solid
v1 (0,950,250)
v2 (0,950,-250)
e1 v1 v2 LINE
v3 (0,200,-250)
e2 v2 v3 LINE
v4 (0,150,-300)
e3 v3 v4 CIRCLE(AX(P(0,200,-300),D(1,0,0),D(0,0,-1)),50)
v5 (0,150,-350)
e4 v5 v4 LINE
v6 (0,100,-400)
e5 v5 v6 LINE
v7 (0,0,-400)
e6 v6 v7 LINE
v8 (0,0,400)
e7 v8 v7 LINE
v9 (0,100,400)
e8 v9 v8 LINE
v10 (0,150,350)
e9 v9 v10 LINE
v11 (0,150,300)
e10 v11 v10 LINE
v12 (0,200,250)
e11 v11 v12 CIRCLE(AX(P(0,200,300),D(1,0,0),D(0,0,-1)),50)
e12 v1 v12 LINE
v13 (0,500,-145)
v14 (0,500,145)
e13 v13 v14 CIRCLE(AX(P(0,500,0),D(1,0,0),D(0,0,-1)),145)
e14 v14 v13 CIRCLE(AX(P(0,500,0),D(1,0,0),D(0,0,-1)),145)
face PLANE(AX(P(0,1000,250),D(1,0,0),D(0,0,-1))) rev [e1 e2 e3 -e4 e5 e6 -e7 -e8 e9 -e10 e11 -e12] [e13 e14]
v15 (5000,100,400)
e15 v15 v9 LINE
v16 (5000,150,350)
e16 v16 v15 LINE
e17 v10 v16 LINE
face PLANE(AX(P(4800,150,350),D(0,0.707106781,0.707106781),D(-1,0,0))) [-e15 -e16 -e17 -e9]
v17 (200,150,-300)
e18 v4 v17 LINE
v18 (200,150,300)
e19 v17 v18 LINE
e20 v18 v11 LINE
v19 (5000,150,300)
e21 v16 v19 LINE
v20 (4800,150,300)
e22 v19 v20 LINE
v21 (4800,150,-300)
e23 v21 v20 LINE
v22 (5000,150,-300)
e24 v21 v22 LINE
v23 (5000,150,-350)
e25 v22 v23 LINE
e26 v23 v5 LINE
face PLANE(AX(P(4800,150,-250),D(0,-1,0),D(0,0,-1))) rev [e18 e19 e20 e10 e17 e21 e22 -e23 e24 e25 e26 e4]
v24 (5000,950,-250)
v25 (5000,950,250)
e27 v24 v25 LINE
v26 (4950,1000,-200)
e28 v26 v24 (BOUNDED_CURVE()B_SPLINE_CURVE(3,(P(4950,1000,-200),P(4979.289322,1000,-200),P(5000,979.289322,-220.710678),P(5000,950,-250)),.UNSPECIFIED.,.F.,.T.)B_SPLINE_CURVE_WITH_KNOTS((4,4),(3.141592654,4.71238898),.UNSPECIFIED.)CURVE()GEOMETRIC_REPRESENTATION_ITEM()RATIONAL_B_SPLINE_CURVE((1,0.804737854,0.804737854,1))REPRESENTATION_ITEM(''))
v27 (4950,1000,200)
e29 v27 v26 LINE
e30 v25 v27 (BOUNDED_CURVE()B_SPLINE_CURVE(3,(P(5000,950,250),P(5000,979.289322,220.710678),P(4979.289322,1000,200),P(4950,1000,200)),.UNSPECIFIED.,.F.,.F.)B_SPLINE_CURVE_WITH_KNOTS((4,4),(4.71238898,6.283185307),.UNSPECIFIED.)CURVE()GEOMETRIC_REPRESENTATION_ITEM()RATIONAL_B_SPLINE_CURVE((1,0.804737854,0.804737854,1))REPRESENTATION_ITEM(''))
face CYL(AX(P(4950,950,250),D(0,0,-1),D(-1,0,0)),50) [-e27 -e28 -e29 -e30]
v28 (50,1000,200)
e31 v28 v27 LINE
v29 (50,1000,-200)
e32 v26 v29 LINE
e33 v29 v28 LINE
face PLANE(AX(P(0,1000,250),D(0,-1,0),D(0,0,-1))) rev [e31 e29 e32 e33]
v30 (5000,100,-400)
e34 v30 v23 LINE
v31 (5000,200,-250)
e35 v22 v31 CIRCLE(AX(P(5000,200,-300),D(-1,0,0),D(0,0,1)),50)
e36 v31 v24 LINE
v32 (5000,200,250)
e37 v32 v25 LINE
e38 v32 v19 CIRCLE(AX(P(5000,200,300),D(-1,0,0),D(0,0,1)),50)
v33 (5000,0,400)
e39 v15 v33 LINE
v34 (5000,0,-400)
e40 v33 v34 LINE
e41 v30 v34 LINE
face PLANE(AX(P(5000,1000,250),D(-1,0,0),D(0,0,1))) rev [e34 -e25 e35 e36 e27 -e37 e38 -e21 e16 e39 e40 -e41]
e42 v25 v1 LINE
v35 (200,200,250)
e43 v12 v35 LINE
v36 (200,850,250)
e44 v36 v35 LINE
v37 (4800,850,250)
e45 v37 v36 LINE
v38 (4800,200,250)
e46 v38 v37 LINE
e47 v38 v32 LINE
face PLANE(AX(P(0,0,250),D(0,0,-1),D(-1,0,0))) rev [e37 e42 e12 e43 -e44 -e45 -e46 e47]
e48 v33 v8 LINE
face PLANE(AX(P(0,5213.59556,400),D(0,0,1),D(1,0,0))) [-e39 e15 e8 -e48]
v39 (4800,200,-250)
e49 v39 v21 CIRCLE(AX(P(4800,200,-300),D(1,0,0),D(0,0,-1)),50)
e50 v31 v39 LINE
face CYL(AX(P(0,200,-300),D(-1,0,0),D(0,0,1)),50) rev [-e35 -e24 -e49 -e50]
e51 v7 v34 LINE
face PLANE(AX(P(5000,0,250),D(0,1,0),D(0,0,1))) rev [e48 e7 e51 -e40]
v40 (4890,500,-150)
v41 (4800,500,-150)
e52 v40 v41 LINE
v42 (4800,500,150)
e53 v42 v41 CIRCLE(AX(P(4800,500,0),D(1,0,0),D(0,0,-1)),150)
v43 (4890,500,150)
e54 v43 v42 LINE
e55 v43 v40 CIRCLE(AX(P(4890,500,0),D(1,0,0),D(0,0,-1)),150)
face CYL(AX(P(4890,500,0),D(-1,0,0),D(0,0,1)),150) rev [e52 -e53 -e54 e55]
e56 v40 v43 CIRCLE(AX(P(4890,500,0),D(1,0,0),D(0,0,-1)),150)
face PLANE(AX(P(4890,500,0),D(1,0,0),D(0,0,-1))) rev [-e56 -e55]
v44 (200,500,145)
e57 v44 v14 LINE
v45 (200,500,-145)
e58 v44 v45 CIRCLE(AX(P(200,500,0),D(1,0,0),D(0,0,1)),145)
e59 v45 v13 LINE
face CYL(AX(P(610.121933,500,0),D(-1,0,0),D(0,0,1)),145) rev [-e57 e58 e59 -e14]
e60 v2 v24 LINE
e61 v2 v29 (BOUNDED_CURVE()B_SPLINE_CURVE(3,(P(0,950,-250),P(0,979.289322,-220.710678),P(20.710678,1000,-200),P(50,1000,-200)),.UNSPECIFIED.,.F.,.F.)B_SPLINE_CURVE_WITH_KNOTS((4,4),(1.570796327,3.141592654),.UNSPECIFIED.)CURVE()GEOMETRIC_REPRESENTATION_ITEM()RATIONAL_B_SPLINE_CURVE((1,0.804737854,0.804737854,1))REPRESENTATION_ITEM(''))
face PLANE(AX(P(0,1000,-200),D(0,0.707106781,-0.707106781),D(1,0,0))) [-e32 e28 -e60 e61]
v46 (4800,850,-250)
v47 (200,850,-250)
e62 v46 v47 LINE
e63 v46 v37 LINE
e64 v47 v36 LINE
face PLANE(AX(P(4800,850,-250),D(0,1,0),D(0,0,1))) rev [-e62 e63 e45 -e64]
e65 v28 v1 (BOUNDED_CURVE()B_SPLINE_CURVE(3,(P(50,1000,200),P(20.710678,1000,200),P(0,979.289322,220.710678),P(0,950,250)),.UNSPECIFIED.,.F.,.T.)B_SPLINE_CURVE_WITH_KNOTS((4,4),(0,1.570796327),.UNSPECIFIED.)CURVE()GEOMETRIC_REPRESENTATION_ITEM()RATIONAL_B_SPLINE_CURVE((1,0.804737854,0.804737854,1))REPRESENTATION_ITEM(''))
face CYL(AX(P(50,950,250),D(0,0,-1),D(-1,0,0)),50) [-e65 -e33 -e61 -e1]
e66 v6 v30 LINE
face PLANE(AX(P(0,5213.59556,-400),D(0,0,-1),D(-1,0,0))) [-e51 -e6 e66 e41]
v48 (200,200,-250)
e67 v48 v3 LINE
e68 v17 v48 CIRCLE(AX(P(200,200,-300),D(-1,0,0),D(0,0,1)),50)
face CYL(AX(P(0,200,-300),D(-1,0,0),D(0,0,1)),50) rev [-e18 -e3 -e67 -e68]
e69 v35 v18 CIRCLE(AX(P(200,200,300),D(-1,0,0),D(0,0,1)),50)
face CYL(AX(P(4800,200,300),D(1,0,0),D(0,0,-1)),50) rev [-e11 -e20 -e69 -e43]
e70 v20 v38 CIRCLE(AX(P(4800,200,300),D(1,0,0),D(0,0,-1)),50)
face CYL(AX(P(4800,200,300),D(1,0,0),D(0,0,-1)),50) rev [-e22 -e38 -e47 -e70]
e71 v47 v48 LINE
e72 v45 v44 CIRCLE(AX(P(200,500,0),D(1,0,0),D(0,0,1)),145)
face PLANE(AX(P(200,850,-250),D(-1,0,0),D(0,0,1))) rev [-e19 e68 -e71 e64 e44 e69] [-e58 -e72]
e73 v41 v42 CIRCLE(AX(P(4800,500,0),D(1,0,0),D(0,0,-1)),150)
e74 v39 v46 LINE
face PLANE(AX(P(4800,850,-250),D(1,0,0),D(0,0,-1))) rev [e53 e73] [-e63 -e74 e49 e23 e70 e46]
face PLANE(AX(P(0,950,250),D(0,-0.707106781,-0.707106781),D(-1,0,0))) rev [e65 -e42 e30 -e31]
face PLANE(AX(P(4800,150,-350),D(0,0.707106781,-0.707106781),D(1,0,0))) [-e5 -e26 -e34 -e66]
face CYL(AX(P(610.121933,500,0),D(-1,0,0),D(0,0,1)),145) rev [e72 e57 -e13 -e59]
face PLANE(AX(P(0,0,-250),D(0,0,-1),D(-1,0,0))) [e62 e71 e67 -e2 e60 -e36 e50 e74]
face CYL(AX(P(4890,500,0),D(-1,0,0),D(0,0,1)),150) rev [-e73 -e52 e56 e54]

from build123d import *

# Parameters (mm, degrees)
SKETCH1_W               = 5000
SKETCH1_H               = 1000
BOSS_EXTRUDE1_DEPTH     = 250
SKETCH2_W               = 4600
SKETCH2_H               = 700
CUT_EXTRUDE1_DEPTH      = 5124.47538298
CUT_EXTRUDE2_DEPTH      = 5106.144464166
CUT_EXTRUDE2_DEPTH_BACK = 200
SKETCH3_R               = 145
SKETCH4_W               = 5000
SKETCH4_H               = 800
BOSS_EXTRUDE2_DEPTH     = 150
CHAMFER1_SIZE           = 50
FILLET1_R               = 50
FILLET2_R               = 50
SKETCH6_R               = 150
CUT_EXTRUDE3_DEPTH      = 90


with BuildPart() as part:
    # Sketch1 → Boss-Extrude1 (new, symmetric)
    with BuildSketch(Plane.XY):
        with Locations((2500, 500)):
            Rectangle(SKETCH1_W, SKETCH1_H)
    extrude(amount=BOSS_EXTRUDE1_DEPTH, both=True)

    # Sketch2 → Cut-Extrude1 (cut, through all)
    with BuildSketch(Plane.XY.offset(250)):
        with Locations((2500, 500)):
            Rectangle(SKETCH2_W, SKETCH2_H)
    extrude(amount=-CUT_EXTRUDE1_DEPTH, mode=Mode.SUBTRACT)

    # Sketch3 → Cut-Extrude2 (cut, two sides: drawn at the far end of the back side and taken through both)
    with BuildSketch(Plane.ZY.offset(-CUT_EXTRUDE2_DEPTH_BACK)):
        with Locations((0, 500)):
            Circle(SKETCH3_R)
    extrude(amount=CUT_EXTRUDE2_DEPTH + CUT_EXTRUDE2_DEPTH_BACK, mode=Mode.SUBTRACT)

    # Sketch4 → Boss-Extrude2 (add)
    with BuildSketch(Plane.XZ):
        with Locations((2500, 0)):
            Rectangle(SKETCH4_W, SKETCH4_H)
    extrude(amount=-BOSS_EXTRUDE2_DEPTH)

    # Chamfer1
    chamfer1_edges = [part.edges().sort_by_distance(p)[0] for p in [
        (2500, 150, 400),
        (2500, 150, -400),
        (2500, 1000, -250),
        (2500, 1000, 250),
    ]]
    chamfer(chamfer1_edges, length=CHAMFER1_SIZE)

    # Fillet1
    fillet1_edges = [part.edges().sort_by_distance(p)[0] for p in [
        (4900, 150, 250),
        (100, 150, 250),
        (4900, 150, -250),
        (100, 150, -250),
    ]]
    fillet(fillet1_edges, radius=FILLET1_R)

    # Fillet2
    fillet2_edges = [part.edges().sort_by_distance(p)[0] for p in [
        (5000, 1000, 0),
        (0, 1000, 0),
    ]]
    fillet(fillet2_edges, radius=FILLET2_R)

    # Sketch6 → Cut-Extrude3 (cut)
    with BuildSketch(Plane(origin=(4800, 0, 0), x_dir=(0, 0, -1), z_dir=(1, 0, 0))):
        with Locations(Location((0, 500, 0), (0, 0, 180))):
            Circle(SKETCH6_R)
    extrude(amount=CUT_EXTRUDE3_DEPTH, mode=Mode.SUBTRACT)


solid = part.part
